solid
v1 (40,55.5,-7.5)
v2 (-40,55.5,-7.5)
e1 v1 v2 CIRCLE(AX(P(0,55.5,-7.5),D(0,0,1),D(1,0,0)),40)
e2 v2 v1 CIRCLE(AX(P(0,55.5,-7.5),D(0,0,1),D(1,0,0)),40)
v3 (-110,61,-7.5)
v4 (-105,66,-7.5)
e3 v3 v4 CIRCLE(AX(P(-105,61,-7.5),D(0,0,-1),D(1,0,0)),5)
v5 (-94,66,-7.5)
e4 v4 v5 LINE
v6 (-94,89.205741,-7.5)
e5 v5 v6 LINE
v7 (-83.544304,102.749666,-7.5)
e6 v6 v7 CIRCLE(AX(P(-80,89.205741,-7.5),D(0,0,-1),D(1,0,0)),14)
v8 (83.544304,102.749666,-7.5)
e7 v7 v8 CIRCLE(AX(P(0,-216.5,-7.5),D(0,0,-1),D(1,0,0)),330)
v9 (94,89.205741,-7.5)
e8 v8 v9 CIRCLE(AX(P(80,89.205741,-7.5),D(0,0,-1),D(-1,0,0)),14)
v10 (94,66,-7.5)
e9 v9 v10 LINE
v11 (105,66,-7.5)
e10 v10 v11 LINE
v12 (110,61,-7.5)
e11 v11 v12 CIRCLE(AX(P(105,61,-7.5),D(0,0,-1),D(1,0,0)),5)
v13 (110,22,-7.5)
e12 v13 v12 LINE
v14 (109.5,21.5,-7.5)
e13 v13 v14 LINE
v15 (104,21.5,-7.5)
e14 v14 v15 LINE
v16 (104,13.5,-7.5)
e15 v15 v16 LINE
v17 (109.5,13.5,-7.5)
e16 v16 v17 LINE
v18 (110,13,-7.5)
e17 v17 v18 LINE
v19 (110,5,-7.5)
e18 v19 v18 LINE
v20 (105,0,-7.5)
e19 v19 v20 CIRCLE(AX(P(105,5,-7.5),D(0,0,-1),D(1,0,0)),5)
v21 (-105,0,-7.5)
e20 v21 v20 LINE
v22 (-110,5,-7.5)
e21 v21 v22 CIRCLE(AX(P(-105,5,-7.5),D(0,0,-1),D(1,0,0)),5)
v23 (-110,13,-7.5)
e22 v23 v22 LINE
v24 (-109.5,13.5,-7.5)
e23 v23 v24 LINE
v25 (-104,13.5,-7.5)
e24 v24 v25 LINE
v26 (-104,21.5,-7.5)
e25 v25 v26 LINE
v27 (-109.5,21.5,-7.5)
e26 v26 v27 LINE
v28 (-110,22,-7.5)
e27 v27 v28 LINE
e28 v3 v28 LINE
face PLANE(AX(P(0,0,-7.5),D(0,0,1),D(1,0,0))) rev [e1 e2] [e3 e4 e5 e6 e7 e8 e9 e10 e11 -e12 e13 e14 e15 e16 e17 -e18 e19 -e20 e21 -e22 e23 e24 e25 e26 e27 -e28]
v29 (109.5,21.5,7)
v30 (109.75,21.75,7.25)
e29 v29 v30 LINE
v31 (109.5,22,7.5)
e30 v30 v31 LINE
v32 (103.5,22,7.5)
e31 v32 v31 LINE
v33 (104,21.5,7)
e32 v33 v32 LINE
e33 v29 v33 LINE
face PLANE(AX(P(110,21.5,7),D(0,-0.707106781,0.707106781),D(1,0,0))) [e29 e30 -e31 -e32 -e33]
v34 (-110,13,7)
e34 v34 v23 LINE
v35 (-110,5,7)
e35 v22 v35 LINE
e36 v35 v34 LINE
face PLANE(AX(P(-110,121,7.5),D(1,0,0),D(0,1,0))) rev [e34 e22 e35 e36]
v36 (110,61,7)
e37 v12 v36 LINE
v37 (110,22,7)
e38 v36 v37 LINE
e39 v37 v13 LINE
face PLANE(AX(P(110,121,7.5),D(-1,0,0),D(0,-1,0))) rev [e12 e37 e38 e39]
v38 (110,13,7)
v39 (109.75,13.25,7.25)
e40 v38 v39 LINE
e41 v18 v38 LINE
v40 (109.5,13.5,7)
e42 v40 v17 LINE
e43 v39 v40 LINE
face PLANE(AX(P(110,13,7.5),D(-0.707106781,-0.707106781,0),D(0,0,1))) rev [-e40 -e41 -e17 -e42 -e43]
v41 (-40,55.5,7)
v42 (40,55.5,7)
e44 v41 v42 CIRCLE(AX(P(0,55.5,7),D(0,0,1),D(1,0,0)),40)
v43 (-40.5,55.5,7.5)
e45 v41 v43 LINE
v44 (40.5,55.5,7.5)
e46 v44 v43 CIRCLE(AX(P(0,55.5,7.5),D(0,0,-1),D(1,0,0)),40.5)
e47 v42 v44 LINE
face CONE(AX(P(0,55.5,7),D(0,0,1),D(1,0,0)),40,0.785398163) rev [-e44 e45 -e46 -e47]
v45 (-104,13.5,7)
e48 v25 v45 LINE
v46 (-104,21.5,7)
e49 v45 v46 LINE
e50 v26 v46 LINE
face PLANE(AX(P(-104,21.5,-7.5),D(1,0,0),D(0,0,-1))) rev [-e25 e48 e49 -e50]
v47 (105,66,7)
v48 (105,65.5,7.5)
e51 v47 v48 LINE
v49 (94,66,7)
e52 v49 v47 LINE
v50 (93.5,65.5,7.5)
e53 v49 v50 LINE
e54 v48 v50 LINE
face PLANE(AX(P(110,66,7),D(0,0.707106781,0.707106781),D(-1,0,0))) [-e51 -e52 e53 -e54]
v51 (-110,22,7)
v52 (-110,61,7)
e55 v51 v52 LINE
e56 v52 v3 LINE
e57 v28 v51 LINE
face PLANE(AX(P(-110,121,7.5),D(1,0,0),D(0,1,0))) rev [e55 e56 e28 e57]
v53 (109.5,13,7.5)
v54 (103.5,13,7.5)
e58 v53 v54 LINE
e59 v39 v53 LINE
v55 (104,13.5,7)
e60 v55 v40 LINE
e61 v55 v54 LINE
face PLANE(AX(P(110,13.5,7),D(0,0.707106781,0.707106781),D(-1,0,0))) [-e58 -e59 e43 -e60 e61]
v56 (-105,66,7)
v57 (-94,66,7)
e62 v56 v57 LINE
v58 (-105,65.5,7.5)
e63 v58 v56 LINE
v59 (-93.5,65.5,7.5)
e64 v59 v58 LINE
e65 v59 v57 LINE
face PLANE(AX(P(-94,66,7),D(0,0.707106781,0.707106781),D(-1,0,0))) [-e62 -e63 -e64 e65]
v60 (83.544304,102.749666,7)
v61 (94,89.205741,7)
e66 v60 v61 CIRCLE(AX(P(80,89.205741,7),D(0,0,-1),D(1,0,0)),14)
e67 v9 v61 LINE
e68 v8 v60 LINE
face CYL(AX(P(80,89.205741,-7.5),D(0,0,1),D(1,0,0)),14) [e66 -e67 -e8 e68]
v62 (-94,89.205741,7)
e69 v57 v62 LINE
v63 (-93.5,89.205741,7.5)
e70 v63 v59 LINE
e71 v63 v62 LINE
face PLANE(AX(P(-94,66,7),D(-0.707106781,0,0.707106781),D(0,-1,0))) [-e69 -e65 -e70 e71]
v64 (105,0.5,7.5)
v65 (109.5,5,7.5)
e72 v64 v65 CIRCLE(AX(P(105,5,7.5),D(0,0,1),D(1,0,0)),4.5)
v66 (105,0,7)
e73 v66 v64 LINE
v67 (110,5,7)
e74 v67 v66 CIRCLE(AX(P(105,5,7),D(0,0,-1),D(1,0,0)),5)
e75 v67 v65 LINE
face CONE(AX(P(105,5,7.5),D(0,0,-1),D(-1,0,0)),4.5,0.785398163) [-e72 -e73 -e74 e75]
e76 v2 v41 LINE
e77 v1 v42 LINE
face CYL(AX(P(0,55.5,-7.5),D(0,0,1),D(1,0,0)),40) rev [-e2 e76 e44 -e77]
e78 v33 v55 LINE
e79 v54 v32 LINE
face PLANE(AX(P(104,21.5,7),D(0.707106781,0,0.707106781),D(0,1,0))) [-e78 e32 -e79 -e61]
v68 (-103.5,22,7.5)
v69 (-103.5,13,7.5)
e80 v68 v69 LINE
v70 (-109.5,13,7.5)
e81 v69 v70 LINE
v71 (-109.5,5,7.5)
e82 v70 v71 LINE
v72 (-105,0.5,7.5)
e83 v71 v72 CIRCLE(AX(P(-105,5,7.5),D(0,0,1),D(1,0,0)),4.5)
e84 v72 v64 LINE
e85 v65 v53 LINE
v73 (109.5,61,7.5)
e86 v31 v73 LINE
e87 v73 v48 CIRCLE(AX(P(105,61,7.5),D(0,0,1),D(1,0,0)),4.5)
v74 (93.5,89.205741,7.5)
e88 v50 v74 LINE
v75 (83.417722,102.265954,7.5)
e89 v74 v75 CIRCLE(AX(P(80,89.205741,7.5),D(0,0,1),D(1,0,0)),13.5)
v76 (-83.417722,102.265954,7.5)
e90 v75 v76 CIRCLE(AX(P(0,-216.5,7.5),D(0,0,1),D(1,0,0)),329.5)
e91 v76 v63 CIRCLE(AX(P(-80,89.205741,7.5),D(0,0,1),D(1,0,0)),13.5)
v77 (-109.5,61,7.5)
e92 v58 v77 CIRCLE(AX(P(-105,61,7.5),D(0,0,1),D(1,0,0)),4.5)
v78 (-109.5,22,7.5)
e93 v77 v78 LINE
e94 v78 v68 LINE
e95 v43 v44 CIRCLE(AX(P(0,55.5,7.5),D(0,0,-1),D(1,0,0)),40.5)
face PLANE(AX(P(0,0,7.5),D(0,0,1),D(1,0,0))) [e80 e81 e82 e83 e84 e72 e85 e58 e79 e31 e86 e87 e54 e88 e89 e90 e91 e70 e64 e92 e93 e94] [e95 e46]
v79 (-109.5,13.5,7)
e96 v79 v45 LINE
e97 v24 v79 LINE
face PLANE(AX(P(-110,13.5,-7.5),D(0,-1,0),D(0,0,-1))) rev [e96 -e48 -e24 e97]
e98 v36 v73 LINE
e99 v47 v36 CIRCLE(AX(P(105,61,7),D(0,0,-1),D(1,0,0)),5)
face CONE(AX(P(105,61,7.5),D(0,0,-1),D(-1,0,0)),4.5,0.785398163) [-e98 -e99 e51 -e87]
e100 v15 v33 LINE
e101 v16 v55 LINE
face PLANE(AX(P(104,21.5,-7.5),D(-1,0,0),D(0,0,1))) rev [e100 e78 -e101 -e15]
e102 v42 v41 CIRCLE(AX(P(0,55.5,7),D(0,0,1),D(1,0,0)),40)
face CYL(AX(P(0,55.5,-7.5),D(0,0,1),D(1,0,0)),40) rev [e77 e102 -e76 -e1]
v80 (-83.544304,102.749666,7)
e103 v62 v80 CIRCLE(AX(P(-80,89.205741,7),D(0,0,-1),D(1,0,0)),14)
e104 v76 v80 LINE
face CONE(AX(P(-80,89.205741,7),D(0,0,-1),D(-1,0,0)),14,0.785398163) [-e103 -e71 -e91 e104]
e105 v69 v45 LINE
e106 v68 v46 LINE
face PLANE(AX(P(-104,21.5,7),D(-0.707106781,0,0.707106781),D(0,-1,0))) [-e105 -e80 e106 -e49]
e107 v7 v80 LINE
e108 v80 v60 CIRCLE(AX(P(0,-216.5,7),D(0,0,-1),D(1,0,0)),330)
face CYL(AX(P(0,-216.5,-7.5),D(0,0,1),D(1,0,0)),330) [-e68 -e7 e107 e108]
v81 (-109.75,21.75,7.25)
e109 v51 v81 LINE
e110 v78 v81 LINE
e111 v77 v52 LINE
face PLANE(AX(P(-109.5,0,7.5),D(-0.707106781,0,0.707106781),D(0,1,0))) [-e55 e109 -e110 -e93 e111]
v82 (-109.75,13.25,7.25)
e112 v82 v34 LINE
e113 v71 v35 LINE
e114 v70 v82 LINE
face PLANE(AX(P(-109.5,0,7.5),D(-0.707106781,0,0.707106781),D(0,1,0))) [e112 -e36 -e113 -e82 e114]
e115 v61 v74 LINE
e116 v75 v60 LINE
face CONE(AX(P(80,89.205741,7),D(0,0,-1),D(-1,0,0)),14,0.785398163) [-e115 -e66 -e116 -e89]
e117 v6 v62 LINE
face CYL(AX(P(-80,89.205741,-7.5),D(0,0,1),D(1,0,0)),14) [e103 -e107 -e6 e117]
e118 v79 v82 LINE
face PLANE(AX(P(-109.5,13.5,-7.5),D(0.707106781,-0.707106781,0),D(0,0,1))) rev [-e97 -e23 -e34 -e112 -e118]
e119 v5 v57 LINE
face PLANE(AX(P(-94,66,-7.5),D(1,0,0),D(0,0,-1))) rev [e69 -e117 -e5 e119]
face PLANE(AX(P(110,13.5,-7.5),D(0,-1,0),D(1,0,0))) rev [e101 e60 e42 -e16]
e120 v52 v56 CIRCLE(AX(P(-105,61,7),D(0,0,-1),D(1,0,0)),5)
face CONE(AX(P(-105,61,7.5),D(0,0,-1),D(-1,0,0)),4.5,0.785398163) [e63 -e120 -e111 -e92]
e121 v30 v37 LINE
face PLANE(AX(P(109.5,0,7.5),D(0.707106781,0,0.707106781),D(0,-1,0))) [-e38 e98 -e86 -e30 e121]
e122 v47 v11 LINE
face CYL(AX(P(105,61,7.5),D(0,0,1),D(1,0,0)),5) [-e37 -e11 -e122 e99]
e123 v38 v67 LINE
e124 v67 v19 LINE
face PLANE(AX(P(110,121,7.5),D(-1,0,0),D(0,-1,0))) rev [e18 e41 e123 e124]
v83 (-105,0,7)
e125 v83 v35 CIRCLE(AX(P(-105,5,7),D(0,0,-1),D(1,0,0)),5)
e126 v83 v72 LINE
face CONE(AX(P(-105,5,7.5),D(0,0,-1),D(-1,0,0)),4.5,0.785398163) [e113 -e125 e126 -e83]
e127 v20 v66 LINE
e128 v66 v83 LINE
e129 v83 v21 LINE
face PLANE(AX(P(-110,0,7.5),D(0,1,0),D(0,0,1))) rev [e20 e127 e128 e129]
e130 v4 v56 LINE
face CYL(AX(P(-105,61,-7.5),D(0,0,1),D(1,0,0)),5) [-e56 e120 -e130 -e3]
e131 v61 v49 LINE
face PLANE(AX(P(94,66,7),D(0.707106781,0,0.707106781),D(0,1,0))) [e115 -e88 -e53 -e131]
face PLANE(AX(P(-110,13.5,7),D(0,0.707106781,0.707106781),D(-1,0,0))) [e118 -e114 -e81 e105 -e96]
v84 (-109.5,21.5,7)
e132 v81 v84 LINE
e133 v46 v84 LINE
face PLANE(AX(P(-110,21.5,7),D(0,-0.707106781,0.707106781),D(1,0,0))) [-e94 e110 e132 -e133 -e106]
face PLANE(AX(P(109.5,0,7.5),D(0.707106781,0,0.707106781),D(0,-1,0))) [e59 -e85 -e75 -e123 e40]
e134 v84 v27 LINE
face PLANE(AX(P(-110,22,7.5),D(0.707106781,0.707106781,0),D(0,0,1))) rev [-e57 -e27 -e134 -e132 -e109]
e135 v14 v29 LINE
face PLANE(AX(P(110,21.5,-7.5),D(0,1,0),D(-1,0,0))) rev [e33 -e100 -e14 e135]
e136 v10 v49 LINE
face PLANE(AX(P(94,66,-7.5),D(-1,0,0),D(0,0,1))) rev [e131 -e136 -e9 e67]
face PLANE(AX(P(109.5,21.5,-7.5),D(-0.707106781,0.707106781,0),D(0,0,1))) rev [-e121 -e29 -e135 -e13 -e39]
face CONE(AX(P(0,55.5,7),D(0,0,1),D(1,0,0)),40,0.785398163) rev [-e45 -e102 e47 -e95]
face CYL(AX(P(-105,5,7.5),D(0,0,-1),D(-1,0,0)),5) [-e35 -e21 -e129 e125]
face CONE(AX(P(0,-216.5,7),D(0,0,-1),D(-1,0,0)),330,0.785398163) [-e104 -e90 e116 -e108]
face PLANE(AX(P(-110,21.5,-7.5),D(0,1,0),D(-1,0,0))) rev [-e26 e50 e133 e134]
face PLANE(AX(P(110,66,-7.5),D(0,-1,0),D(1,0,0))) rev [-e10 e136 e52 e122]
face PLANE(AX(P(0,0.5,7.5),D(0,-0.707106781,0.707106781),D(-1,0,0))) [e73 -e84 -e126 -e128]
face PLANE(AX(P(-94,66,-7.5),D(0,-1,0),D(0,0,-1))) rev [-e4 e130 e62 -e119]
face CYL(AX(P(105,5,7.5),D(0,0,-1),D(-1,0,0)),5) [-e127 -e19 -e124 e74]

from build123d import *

# Parameters (mm, degrees)
SKETCH_1_W           = 220
SKETCH_1_H           = 121
EXTRUDE_1_DEPTH      = 7.5
SKETCH_5_W           = 6
SKETCH_5_H           = 8
CUT_EXTRUDE_2_DEPTH  = 165.213275955
SKETCH_9_R           = 22.5
CUT_EXTRUDE_5_DEPTH  = 10
CUT_EXTRUDE_12_DEPTH = 165.213275955
FILLET_1_R           = 5
CHAMFER_1_SIZE       = 0.5
SKETCH_19_R          = 40
CUT_EXTRUDE_13_DEPTH = 159.767912375
CHAMFER_2_SIZE       = 0.5
CHAMFER_4_SIZE       = 0.5


with BuildPart() as part:
    # 草图1 → 凸台-拉伸1 (new, symmetric)
    with BuildSketch(Plane.XY):
        with Locations((0, 60.5)):
            Rectangle(SKETCH_1_W, SKETCH_1_H)
    extrude(amount=EXTRUDE_1_DEPTH, both=True)

    # 草图5 → 切除-拉伸2 (cut, through all)
    with BuildSketch(Plane.XY.offset(7.5)):
        with Locations((-107, 17.5)):
            Rectangle(SKETCH_5_W, SKETCH_5_H)
        with Locations((107, 17.5)):
            Rectangle(SKETCH_5_W, SKETCH_5_H)
    extrude(amount=-CUT_EXTRUDE_2_DEPTH, mode=Mode.SUBTRACT)

    # 草图9 → 切除-拉伸5 (cut)
    with BuildSketch(Plane(origin=(0, 0, -7.5), x_dir=(-1, 0, 0), z_dir=(0, 0, -1))):
        with Locations((0, 66.5)):
            Circle(SKETCH_9_R)
    extrude(amount=-CUT_EXTRUDE_5_DEPTH, mode=Mode.SUBTRACT)

    # 草图4 → 切除-拉伸12 (cut, through all)
    with BuildSketch(Plane.XY.offset(7.5)):
        with BuildLine():
            Line((-94, 66), (-110, 66))
            Line((-110, 66), (-110, 122.2))
            Line((-110, 122.2), (110, 122.2))
            Line((110, 122.2), (110, 66))
            Line((110, 66), (94, 66))
            Line((94, 66), (94, 89.205740869))
            ThreePointArc((94, 89.205740869), (91.081973046, 97.760848899), (83.544303797, 102.749666097))
            ThreePointArc((83.544303797, 102.749666097), (0, 113.5), (-83.544303797, 102.749666097))
            ThreePointArc((-83.544303797, 102.749666097), (-91.081973046, 97.760848899), (-94, 89.205740869))
            Line((-94, 89.205740869), (-94, 66))
        make_face()
    extrude(amount=-CUT_EXTRUDE_12_DEPTH, mode=Mode.SUBTRACT)

    # 圆角1
    fillet_1_edges = [part.edges().sort_by_distance(p)[0] for p in [
        (-110, 66, 0),
        (110, 66, 0),
        (110, 0, 0),
        (-110, 0, 0),
    ]]
    fillet(fillet_1_edges, radius=FILLET_1_R)

    # 倒角1
    chamfer_1_edges = [part.edges().sort_by_distance(p)[0] for p in [
        (-110, 9.25, 7.5),
        (-107, 13.5, 7.5),
        (-104, 17.5, 7.5),
        (-107, 21.5, 7.5),
        (110, 41.25, 7.5),
        (107, 21.5, 7.5),
        (104, 17.5, 7.5),
        (107, 13.5, 7.5),
        (-94, 77.602870434, 7.5),
        (-91.081973046, 97.760848899, 7.5),
        (0, 113.5, 7.5),
        (91.081973046, 97.760848899, 7.5),
        (94, 77.602870434, 7.5),
        (99.5, 66, 7.5),
        (110, 9.25, 7.5),
        (0, 0, 7.5),
        (-99.5, 66, 7.5),
        (-110, 41.25, 7.5),
        (-108.535533906, 64.535533906, 7.5),
        (108.535533906, 64.535533906, 7.5),
        (-108.535533906, 1.464466094, 7.5),
        (108.535533906, 1.464466094, 7.5),
    ]]
    chamfer(chamfer_1_edges, length=CHAMFER_1_SIZE)

    # 草图19 → 切除-拉伸13 (cut, through all)
    with BuildSketch(Plane.XY.offset(7.5)):
        with Locations((0, 55.5)):
            Circle(SKETCH_19_R)
    extrude(amount=-CUT_EXTRUDE_13_DEPTH, mode=Mode.SUBTRACT)

    # 倒角2
    chamfer_2_edges = [part.edges().sort_by_distance(p)[0] for p in [
        (-40, 55.5, 7.5),
    ]]
    chamfer(chamfer_2_edges, length=CHAMFER_2_SIZE)

    # 倒角4
    chamfer_4_edges = [part.edges().sort_by_distance(p)[0] for p in [
        (-110, 13.5, -0.25),
        (-110, 21.5, -0.25),
        (110, 21.5, -0.25),
        (110, 13.5, -0.25),
    ]]
    chamfer(chamfer_4_edges, length=CHAMFER_4_SIZE)


solid = part.part
